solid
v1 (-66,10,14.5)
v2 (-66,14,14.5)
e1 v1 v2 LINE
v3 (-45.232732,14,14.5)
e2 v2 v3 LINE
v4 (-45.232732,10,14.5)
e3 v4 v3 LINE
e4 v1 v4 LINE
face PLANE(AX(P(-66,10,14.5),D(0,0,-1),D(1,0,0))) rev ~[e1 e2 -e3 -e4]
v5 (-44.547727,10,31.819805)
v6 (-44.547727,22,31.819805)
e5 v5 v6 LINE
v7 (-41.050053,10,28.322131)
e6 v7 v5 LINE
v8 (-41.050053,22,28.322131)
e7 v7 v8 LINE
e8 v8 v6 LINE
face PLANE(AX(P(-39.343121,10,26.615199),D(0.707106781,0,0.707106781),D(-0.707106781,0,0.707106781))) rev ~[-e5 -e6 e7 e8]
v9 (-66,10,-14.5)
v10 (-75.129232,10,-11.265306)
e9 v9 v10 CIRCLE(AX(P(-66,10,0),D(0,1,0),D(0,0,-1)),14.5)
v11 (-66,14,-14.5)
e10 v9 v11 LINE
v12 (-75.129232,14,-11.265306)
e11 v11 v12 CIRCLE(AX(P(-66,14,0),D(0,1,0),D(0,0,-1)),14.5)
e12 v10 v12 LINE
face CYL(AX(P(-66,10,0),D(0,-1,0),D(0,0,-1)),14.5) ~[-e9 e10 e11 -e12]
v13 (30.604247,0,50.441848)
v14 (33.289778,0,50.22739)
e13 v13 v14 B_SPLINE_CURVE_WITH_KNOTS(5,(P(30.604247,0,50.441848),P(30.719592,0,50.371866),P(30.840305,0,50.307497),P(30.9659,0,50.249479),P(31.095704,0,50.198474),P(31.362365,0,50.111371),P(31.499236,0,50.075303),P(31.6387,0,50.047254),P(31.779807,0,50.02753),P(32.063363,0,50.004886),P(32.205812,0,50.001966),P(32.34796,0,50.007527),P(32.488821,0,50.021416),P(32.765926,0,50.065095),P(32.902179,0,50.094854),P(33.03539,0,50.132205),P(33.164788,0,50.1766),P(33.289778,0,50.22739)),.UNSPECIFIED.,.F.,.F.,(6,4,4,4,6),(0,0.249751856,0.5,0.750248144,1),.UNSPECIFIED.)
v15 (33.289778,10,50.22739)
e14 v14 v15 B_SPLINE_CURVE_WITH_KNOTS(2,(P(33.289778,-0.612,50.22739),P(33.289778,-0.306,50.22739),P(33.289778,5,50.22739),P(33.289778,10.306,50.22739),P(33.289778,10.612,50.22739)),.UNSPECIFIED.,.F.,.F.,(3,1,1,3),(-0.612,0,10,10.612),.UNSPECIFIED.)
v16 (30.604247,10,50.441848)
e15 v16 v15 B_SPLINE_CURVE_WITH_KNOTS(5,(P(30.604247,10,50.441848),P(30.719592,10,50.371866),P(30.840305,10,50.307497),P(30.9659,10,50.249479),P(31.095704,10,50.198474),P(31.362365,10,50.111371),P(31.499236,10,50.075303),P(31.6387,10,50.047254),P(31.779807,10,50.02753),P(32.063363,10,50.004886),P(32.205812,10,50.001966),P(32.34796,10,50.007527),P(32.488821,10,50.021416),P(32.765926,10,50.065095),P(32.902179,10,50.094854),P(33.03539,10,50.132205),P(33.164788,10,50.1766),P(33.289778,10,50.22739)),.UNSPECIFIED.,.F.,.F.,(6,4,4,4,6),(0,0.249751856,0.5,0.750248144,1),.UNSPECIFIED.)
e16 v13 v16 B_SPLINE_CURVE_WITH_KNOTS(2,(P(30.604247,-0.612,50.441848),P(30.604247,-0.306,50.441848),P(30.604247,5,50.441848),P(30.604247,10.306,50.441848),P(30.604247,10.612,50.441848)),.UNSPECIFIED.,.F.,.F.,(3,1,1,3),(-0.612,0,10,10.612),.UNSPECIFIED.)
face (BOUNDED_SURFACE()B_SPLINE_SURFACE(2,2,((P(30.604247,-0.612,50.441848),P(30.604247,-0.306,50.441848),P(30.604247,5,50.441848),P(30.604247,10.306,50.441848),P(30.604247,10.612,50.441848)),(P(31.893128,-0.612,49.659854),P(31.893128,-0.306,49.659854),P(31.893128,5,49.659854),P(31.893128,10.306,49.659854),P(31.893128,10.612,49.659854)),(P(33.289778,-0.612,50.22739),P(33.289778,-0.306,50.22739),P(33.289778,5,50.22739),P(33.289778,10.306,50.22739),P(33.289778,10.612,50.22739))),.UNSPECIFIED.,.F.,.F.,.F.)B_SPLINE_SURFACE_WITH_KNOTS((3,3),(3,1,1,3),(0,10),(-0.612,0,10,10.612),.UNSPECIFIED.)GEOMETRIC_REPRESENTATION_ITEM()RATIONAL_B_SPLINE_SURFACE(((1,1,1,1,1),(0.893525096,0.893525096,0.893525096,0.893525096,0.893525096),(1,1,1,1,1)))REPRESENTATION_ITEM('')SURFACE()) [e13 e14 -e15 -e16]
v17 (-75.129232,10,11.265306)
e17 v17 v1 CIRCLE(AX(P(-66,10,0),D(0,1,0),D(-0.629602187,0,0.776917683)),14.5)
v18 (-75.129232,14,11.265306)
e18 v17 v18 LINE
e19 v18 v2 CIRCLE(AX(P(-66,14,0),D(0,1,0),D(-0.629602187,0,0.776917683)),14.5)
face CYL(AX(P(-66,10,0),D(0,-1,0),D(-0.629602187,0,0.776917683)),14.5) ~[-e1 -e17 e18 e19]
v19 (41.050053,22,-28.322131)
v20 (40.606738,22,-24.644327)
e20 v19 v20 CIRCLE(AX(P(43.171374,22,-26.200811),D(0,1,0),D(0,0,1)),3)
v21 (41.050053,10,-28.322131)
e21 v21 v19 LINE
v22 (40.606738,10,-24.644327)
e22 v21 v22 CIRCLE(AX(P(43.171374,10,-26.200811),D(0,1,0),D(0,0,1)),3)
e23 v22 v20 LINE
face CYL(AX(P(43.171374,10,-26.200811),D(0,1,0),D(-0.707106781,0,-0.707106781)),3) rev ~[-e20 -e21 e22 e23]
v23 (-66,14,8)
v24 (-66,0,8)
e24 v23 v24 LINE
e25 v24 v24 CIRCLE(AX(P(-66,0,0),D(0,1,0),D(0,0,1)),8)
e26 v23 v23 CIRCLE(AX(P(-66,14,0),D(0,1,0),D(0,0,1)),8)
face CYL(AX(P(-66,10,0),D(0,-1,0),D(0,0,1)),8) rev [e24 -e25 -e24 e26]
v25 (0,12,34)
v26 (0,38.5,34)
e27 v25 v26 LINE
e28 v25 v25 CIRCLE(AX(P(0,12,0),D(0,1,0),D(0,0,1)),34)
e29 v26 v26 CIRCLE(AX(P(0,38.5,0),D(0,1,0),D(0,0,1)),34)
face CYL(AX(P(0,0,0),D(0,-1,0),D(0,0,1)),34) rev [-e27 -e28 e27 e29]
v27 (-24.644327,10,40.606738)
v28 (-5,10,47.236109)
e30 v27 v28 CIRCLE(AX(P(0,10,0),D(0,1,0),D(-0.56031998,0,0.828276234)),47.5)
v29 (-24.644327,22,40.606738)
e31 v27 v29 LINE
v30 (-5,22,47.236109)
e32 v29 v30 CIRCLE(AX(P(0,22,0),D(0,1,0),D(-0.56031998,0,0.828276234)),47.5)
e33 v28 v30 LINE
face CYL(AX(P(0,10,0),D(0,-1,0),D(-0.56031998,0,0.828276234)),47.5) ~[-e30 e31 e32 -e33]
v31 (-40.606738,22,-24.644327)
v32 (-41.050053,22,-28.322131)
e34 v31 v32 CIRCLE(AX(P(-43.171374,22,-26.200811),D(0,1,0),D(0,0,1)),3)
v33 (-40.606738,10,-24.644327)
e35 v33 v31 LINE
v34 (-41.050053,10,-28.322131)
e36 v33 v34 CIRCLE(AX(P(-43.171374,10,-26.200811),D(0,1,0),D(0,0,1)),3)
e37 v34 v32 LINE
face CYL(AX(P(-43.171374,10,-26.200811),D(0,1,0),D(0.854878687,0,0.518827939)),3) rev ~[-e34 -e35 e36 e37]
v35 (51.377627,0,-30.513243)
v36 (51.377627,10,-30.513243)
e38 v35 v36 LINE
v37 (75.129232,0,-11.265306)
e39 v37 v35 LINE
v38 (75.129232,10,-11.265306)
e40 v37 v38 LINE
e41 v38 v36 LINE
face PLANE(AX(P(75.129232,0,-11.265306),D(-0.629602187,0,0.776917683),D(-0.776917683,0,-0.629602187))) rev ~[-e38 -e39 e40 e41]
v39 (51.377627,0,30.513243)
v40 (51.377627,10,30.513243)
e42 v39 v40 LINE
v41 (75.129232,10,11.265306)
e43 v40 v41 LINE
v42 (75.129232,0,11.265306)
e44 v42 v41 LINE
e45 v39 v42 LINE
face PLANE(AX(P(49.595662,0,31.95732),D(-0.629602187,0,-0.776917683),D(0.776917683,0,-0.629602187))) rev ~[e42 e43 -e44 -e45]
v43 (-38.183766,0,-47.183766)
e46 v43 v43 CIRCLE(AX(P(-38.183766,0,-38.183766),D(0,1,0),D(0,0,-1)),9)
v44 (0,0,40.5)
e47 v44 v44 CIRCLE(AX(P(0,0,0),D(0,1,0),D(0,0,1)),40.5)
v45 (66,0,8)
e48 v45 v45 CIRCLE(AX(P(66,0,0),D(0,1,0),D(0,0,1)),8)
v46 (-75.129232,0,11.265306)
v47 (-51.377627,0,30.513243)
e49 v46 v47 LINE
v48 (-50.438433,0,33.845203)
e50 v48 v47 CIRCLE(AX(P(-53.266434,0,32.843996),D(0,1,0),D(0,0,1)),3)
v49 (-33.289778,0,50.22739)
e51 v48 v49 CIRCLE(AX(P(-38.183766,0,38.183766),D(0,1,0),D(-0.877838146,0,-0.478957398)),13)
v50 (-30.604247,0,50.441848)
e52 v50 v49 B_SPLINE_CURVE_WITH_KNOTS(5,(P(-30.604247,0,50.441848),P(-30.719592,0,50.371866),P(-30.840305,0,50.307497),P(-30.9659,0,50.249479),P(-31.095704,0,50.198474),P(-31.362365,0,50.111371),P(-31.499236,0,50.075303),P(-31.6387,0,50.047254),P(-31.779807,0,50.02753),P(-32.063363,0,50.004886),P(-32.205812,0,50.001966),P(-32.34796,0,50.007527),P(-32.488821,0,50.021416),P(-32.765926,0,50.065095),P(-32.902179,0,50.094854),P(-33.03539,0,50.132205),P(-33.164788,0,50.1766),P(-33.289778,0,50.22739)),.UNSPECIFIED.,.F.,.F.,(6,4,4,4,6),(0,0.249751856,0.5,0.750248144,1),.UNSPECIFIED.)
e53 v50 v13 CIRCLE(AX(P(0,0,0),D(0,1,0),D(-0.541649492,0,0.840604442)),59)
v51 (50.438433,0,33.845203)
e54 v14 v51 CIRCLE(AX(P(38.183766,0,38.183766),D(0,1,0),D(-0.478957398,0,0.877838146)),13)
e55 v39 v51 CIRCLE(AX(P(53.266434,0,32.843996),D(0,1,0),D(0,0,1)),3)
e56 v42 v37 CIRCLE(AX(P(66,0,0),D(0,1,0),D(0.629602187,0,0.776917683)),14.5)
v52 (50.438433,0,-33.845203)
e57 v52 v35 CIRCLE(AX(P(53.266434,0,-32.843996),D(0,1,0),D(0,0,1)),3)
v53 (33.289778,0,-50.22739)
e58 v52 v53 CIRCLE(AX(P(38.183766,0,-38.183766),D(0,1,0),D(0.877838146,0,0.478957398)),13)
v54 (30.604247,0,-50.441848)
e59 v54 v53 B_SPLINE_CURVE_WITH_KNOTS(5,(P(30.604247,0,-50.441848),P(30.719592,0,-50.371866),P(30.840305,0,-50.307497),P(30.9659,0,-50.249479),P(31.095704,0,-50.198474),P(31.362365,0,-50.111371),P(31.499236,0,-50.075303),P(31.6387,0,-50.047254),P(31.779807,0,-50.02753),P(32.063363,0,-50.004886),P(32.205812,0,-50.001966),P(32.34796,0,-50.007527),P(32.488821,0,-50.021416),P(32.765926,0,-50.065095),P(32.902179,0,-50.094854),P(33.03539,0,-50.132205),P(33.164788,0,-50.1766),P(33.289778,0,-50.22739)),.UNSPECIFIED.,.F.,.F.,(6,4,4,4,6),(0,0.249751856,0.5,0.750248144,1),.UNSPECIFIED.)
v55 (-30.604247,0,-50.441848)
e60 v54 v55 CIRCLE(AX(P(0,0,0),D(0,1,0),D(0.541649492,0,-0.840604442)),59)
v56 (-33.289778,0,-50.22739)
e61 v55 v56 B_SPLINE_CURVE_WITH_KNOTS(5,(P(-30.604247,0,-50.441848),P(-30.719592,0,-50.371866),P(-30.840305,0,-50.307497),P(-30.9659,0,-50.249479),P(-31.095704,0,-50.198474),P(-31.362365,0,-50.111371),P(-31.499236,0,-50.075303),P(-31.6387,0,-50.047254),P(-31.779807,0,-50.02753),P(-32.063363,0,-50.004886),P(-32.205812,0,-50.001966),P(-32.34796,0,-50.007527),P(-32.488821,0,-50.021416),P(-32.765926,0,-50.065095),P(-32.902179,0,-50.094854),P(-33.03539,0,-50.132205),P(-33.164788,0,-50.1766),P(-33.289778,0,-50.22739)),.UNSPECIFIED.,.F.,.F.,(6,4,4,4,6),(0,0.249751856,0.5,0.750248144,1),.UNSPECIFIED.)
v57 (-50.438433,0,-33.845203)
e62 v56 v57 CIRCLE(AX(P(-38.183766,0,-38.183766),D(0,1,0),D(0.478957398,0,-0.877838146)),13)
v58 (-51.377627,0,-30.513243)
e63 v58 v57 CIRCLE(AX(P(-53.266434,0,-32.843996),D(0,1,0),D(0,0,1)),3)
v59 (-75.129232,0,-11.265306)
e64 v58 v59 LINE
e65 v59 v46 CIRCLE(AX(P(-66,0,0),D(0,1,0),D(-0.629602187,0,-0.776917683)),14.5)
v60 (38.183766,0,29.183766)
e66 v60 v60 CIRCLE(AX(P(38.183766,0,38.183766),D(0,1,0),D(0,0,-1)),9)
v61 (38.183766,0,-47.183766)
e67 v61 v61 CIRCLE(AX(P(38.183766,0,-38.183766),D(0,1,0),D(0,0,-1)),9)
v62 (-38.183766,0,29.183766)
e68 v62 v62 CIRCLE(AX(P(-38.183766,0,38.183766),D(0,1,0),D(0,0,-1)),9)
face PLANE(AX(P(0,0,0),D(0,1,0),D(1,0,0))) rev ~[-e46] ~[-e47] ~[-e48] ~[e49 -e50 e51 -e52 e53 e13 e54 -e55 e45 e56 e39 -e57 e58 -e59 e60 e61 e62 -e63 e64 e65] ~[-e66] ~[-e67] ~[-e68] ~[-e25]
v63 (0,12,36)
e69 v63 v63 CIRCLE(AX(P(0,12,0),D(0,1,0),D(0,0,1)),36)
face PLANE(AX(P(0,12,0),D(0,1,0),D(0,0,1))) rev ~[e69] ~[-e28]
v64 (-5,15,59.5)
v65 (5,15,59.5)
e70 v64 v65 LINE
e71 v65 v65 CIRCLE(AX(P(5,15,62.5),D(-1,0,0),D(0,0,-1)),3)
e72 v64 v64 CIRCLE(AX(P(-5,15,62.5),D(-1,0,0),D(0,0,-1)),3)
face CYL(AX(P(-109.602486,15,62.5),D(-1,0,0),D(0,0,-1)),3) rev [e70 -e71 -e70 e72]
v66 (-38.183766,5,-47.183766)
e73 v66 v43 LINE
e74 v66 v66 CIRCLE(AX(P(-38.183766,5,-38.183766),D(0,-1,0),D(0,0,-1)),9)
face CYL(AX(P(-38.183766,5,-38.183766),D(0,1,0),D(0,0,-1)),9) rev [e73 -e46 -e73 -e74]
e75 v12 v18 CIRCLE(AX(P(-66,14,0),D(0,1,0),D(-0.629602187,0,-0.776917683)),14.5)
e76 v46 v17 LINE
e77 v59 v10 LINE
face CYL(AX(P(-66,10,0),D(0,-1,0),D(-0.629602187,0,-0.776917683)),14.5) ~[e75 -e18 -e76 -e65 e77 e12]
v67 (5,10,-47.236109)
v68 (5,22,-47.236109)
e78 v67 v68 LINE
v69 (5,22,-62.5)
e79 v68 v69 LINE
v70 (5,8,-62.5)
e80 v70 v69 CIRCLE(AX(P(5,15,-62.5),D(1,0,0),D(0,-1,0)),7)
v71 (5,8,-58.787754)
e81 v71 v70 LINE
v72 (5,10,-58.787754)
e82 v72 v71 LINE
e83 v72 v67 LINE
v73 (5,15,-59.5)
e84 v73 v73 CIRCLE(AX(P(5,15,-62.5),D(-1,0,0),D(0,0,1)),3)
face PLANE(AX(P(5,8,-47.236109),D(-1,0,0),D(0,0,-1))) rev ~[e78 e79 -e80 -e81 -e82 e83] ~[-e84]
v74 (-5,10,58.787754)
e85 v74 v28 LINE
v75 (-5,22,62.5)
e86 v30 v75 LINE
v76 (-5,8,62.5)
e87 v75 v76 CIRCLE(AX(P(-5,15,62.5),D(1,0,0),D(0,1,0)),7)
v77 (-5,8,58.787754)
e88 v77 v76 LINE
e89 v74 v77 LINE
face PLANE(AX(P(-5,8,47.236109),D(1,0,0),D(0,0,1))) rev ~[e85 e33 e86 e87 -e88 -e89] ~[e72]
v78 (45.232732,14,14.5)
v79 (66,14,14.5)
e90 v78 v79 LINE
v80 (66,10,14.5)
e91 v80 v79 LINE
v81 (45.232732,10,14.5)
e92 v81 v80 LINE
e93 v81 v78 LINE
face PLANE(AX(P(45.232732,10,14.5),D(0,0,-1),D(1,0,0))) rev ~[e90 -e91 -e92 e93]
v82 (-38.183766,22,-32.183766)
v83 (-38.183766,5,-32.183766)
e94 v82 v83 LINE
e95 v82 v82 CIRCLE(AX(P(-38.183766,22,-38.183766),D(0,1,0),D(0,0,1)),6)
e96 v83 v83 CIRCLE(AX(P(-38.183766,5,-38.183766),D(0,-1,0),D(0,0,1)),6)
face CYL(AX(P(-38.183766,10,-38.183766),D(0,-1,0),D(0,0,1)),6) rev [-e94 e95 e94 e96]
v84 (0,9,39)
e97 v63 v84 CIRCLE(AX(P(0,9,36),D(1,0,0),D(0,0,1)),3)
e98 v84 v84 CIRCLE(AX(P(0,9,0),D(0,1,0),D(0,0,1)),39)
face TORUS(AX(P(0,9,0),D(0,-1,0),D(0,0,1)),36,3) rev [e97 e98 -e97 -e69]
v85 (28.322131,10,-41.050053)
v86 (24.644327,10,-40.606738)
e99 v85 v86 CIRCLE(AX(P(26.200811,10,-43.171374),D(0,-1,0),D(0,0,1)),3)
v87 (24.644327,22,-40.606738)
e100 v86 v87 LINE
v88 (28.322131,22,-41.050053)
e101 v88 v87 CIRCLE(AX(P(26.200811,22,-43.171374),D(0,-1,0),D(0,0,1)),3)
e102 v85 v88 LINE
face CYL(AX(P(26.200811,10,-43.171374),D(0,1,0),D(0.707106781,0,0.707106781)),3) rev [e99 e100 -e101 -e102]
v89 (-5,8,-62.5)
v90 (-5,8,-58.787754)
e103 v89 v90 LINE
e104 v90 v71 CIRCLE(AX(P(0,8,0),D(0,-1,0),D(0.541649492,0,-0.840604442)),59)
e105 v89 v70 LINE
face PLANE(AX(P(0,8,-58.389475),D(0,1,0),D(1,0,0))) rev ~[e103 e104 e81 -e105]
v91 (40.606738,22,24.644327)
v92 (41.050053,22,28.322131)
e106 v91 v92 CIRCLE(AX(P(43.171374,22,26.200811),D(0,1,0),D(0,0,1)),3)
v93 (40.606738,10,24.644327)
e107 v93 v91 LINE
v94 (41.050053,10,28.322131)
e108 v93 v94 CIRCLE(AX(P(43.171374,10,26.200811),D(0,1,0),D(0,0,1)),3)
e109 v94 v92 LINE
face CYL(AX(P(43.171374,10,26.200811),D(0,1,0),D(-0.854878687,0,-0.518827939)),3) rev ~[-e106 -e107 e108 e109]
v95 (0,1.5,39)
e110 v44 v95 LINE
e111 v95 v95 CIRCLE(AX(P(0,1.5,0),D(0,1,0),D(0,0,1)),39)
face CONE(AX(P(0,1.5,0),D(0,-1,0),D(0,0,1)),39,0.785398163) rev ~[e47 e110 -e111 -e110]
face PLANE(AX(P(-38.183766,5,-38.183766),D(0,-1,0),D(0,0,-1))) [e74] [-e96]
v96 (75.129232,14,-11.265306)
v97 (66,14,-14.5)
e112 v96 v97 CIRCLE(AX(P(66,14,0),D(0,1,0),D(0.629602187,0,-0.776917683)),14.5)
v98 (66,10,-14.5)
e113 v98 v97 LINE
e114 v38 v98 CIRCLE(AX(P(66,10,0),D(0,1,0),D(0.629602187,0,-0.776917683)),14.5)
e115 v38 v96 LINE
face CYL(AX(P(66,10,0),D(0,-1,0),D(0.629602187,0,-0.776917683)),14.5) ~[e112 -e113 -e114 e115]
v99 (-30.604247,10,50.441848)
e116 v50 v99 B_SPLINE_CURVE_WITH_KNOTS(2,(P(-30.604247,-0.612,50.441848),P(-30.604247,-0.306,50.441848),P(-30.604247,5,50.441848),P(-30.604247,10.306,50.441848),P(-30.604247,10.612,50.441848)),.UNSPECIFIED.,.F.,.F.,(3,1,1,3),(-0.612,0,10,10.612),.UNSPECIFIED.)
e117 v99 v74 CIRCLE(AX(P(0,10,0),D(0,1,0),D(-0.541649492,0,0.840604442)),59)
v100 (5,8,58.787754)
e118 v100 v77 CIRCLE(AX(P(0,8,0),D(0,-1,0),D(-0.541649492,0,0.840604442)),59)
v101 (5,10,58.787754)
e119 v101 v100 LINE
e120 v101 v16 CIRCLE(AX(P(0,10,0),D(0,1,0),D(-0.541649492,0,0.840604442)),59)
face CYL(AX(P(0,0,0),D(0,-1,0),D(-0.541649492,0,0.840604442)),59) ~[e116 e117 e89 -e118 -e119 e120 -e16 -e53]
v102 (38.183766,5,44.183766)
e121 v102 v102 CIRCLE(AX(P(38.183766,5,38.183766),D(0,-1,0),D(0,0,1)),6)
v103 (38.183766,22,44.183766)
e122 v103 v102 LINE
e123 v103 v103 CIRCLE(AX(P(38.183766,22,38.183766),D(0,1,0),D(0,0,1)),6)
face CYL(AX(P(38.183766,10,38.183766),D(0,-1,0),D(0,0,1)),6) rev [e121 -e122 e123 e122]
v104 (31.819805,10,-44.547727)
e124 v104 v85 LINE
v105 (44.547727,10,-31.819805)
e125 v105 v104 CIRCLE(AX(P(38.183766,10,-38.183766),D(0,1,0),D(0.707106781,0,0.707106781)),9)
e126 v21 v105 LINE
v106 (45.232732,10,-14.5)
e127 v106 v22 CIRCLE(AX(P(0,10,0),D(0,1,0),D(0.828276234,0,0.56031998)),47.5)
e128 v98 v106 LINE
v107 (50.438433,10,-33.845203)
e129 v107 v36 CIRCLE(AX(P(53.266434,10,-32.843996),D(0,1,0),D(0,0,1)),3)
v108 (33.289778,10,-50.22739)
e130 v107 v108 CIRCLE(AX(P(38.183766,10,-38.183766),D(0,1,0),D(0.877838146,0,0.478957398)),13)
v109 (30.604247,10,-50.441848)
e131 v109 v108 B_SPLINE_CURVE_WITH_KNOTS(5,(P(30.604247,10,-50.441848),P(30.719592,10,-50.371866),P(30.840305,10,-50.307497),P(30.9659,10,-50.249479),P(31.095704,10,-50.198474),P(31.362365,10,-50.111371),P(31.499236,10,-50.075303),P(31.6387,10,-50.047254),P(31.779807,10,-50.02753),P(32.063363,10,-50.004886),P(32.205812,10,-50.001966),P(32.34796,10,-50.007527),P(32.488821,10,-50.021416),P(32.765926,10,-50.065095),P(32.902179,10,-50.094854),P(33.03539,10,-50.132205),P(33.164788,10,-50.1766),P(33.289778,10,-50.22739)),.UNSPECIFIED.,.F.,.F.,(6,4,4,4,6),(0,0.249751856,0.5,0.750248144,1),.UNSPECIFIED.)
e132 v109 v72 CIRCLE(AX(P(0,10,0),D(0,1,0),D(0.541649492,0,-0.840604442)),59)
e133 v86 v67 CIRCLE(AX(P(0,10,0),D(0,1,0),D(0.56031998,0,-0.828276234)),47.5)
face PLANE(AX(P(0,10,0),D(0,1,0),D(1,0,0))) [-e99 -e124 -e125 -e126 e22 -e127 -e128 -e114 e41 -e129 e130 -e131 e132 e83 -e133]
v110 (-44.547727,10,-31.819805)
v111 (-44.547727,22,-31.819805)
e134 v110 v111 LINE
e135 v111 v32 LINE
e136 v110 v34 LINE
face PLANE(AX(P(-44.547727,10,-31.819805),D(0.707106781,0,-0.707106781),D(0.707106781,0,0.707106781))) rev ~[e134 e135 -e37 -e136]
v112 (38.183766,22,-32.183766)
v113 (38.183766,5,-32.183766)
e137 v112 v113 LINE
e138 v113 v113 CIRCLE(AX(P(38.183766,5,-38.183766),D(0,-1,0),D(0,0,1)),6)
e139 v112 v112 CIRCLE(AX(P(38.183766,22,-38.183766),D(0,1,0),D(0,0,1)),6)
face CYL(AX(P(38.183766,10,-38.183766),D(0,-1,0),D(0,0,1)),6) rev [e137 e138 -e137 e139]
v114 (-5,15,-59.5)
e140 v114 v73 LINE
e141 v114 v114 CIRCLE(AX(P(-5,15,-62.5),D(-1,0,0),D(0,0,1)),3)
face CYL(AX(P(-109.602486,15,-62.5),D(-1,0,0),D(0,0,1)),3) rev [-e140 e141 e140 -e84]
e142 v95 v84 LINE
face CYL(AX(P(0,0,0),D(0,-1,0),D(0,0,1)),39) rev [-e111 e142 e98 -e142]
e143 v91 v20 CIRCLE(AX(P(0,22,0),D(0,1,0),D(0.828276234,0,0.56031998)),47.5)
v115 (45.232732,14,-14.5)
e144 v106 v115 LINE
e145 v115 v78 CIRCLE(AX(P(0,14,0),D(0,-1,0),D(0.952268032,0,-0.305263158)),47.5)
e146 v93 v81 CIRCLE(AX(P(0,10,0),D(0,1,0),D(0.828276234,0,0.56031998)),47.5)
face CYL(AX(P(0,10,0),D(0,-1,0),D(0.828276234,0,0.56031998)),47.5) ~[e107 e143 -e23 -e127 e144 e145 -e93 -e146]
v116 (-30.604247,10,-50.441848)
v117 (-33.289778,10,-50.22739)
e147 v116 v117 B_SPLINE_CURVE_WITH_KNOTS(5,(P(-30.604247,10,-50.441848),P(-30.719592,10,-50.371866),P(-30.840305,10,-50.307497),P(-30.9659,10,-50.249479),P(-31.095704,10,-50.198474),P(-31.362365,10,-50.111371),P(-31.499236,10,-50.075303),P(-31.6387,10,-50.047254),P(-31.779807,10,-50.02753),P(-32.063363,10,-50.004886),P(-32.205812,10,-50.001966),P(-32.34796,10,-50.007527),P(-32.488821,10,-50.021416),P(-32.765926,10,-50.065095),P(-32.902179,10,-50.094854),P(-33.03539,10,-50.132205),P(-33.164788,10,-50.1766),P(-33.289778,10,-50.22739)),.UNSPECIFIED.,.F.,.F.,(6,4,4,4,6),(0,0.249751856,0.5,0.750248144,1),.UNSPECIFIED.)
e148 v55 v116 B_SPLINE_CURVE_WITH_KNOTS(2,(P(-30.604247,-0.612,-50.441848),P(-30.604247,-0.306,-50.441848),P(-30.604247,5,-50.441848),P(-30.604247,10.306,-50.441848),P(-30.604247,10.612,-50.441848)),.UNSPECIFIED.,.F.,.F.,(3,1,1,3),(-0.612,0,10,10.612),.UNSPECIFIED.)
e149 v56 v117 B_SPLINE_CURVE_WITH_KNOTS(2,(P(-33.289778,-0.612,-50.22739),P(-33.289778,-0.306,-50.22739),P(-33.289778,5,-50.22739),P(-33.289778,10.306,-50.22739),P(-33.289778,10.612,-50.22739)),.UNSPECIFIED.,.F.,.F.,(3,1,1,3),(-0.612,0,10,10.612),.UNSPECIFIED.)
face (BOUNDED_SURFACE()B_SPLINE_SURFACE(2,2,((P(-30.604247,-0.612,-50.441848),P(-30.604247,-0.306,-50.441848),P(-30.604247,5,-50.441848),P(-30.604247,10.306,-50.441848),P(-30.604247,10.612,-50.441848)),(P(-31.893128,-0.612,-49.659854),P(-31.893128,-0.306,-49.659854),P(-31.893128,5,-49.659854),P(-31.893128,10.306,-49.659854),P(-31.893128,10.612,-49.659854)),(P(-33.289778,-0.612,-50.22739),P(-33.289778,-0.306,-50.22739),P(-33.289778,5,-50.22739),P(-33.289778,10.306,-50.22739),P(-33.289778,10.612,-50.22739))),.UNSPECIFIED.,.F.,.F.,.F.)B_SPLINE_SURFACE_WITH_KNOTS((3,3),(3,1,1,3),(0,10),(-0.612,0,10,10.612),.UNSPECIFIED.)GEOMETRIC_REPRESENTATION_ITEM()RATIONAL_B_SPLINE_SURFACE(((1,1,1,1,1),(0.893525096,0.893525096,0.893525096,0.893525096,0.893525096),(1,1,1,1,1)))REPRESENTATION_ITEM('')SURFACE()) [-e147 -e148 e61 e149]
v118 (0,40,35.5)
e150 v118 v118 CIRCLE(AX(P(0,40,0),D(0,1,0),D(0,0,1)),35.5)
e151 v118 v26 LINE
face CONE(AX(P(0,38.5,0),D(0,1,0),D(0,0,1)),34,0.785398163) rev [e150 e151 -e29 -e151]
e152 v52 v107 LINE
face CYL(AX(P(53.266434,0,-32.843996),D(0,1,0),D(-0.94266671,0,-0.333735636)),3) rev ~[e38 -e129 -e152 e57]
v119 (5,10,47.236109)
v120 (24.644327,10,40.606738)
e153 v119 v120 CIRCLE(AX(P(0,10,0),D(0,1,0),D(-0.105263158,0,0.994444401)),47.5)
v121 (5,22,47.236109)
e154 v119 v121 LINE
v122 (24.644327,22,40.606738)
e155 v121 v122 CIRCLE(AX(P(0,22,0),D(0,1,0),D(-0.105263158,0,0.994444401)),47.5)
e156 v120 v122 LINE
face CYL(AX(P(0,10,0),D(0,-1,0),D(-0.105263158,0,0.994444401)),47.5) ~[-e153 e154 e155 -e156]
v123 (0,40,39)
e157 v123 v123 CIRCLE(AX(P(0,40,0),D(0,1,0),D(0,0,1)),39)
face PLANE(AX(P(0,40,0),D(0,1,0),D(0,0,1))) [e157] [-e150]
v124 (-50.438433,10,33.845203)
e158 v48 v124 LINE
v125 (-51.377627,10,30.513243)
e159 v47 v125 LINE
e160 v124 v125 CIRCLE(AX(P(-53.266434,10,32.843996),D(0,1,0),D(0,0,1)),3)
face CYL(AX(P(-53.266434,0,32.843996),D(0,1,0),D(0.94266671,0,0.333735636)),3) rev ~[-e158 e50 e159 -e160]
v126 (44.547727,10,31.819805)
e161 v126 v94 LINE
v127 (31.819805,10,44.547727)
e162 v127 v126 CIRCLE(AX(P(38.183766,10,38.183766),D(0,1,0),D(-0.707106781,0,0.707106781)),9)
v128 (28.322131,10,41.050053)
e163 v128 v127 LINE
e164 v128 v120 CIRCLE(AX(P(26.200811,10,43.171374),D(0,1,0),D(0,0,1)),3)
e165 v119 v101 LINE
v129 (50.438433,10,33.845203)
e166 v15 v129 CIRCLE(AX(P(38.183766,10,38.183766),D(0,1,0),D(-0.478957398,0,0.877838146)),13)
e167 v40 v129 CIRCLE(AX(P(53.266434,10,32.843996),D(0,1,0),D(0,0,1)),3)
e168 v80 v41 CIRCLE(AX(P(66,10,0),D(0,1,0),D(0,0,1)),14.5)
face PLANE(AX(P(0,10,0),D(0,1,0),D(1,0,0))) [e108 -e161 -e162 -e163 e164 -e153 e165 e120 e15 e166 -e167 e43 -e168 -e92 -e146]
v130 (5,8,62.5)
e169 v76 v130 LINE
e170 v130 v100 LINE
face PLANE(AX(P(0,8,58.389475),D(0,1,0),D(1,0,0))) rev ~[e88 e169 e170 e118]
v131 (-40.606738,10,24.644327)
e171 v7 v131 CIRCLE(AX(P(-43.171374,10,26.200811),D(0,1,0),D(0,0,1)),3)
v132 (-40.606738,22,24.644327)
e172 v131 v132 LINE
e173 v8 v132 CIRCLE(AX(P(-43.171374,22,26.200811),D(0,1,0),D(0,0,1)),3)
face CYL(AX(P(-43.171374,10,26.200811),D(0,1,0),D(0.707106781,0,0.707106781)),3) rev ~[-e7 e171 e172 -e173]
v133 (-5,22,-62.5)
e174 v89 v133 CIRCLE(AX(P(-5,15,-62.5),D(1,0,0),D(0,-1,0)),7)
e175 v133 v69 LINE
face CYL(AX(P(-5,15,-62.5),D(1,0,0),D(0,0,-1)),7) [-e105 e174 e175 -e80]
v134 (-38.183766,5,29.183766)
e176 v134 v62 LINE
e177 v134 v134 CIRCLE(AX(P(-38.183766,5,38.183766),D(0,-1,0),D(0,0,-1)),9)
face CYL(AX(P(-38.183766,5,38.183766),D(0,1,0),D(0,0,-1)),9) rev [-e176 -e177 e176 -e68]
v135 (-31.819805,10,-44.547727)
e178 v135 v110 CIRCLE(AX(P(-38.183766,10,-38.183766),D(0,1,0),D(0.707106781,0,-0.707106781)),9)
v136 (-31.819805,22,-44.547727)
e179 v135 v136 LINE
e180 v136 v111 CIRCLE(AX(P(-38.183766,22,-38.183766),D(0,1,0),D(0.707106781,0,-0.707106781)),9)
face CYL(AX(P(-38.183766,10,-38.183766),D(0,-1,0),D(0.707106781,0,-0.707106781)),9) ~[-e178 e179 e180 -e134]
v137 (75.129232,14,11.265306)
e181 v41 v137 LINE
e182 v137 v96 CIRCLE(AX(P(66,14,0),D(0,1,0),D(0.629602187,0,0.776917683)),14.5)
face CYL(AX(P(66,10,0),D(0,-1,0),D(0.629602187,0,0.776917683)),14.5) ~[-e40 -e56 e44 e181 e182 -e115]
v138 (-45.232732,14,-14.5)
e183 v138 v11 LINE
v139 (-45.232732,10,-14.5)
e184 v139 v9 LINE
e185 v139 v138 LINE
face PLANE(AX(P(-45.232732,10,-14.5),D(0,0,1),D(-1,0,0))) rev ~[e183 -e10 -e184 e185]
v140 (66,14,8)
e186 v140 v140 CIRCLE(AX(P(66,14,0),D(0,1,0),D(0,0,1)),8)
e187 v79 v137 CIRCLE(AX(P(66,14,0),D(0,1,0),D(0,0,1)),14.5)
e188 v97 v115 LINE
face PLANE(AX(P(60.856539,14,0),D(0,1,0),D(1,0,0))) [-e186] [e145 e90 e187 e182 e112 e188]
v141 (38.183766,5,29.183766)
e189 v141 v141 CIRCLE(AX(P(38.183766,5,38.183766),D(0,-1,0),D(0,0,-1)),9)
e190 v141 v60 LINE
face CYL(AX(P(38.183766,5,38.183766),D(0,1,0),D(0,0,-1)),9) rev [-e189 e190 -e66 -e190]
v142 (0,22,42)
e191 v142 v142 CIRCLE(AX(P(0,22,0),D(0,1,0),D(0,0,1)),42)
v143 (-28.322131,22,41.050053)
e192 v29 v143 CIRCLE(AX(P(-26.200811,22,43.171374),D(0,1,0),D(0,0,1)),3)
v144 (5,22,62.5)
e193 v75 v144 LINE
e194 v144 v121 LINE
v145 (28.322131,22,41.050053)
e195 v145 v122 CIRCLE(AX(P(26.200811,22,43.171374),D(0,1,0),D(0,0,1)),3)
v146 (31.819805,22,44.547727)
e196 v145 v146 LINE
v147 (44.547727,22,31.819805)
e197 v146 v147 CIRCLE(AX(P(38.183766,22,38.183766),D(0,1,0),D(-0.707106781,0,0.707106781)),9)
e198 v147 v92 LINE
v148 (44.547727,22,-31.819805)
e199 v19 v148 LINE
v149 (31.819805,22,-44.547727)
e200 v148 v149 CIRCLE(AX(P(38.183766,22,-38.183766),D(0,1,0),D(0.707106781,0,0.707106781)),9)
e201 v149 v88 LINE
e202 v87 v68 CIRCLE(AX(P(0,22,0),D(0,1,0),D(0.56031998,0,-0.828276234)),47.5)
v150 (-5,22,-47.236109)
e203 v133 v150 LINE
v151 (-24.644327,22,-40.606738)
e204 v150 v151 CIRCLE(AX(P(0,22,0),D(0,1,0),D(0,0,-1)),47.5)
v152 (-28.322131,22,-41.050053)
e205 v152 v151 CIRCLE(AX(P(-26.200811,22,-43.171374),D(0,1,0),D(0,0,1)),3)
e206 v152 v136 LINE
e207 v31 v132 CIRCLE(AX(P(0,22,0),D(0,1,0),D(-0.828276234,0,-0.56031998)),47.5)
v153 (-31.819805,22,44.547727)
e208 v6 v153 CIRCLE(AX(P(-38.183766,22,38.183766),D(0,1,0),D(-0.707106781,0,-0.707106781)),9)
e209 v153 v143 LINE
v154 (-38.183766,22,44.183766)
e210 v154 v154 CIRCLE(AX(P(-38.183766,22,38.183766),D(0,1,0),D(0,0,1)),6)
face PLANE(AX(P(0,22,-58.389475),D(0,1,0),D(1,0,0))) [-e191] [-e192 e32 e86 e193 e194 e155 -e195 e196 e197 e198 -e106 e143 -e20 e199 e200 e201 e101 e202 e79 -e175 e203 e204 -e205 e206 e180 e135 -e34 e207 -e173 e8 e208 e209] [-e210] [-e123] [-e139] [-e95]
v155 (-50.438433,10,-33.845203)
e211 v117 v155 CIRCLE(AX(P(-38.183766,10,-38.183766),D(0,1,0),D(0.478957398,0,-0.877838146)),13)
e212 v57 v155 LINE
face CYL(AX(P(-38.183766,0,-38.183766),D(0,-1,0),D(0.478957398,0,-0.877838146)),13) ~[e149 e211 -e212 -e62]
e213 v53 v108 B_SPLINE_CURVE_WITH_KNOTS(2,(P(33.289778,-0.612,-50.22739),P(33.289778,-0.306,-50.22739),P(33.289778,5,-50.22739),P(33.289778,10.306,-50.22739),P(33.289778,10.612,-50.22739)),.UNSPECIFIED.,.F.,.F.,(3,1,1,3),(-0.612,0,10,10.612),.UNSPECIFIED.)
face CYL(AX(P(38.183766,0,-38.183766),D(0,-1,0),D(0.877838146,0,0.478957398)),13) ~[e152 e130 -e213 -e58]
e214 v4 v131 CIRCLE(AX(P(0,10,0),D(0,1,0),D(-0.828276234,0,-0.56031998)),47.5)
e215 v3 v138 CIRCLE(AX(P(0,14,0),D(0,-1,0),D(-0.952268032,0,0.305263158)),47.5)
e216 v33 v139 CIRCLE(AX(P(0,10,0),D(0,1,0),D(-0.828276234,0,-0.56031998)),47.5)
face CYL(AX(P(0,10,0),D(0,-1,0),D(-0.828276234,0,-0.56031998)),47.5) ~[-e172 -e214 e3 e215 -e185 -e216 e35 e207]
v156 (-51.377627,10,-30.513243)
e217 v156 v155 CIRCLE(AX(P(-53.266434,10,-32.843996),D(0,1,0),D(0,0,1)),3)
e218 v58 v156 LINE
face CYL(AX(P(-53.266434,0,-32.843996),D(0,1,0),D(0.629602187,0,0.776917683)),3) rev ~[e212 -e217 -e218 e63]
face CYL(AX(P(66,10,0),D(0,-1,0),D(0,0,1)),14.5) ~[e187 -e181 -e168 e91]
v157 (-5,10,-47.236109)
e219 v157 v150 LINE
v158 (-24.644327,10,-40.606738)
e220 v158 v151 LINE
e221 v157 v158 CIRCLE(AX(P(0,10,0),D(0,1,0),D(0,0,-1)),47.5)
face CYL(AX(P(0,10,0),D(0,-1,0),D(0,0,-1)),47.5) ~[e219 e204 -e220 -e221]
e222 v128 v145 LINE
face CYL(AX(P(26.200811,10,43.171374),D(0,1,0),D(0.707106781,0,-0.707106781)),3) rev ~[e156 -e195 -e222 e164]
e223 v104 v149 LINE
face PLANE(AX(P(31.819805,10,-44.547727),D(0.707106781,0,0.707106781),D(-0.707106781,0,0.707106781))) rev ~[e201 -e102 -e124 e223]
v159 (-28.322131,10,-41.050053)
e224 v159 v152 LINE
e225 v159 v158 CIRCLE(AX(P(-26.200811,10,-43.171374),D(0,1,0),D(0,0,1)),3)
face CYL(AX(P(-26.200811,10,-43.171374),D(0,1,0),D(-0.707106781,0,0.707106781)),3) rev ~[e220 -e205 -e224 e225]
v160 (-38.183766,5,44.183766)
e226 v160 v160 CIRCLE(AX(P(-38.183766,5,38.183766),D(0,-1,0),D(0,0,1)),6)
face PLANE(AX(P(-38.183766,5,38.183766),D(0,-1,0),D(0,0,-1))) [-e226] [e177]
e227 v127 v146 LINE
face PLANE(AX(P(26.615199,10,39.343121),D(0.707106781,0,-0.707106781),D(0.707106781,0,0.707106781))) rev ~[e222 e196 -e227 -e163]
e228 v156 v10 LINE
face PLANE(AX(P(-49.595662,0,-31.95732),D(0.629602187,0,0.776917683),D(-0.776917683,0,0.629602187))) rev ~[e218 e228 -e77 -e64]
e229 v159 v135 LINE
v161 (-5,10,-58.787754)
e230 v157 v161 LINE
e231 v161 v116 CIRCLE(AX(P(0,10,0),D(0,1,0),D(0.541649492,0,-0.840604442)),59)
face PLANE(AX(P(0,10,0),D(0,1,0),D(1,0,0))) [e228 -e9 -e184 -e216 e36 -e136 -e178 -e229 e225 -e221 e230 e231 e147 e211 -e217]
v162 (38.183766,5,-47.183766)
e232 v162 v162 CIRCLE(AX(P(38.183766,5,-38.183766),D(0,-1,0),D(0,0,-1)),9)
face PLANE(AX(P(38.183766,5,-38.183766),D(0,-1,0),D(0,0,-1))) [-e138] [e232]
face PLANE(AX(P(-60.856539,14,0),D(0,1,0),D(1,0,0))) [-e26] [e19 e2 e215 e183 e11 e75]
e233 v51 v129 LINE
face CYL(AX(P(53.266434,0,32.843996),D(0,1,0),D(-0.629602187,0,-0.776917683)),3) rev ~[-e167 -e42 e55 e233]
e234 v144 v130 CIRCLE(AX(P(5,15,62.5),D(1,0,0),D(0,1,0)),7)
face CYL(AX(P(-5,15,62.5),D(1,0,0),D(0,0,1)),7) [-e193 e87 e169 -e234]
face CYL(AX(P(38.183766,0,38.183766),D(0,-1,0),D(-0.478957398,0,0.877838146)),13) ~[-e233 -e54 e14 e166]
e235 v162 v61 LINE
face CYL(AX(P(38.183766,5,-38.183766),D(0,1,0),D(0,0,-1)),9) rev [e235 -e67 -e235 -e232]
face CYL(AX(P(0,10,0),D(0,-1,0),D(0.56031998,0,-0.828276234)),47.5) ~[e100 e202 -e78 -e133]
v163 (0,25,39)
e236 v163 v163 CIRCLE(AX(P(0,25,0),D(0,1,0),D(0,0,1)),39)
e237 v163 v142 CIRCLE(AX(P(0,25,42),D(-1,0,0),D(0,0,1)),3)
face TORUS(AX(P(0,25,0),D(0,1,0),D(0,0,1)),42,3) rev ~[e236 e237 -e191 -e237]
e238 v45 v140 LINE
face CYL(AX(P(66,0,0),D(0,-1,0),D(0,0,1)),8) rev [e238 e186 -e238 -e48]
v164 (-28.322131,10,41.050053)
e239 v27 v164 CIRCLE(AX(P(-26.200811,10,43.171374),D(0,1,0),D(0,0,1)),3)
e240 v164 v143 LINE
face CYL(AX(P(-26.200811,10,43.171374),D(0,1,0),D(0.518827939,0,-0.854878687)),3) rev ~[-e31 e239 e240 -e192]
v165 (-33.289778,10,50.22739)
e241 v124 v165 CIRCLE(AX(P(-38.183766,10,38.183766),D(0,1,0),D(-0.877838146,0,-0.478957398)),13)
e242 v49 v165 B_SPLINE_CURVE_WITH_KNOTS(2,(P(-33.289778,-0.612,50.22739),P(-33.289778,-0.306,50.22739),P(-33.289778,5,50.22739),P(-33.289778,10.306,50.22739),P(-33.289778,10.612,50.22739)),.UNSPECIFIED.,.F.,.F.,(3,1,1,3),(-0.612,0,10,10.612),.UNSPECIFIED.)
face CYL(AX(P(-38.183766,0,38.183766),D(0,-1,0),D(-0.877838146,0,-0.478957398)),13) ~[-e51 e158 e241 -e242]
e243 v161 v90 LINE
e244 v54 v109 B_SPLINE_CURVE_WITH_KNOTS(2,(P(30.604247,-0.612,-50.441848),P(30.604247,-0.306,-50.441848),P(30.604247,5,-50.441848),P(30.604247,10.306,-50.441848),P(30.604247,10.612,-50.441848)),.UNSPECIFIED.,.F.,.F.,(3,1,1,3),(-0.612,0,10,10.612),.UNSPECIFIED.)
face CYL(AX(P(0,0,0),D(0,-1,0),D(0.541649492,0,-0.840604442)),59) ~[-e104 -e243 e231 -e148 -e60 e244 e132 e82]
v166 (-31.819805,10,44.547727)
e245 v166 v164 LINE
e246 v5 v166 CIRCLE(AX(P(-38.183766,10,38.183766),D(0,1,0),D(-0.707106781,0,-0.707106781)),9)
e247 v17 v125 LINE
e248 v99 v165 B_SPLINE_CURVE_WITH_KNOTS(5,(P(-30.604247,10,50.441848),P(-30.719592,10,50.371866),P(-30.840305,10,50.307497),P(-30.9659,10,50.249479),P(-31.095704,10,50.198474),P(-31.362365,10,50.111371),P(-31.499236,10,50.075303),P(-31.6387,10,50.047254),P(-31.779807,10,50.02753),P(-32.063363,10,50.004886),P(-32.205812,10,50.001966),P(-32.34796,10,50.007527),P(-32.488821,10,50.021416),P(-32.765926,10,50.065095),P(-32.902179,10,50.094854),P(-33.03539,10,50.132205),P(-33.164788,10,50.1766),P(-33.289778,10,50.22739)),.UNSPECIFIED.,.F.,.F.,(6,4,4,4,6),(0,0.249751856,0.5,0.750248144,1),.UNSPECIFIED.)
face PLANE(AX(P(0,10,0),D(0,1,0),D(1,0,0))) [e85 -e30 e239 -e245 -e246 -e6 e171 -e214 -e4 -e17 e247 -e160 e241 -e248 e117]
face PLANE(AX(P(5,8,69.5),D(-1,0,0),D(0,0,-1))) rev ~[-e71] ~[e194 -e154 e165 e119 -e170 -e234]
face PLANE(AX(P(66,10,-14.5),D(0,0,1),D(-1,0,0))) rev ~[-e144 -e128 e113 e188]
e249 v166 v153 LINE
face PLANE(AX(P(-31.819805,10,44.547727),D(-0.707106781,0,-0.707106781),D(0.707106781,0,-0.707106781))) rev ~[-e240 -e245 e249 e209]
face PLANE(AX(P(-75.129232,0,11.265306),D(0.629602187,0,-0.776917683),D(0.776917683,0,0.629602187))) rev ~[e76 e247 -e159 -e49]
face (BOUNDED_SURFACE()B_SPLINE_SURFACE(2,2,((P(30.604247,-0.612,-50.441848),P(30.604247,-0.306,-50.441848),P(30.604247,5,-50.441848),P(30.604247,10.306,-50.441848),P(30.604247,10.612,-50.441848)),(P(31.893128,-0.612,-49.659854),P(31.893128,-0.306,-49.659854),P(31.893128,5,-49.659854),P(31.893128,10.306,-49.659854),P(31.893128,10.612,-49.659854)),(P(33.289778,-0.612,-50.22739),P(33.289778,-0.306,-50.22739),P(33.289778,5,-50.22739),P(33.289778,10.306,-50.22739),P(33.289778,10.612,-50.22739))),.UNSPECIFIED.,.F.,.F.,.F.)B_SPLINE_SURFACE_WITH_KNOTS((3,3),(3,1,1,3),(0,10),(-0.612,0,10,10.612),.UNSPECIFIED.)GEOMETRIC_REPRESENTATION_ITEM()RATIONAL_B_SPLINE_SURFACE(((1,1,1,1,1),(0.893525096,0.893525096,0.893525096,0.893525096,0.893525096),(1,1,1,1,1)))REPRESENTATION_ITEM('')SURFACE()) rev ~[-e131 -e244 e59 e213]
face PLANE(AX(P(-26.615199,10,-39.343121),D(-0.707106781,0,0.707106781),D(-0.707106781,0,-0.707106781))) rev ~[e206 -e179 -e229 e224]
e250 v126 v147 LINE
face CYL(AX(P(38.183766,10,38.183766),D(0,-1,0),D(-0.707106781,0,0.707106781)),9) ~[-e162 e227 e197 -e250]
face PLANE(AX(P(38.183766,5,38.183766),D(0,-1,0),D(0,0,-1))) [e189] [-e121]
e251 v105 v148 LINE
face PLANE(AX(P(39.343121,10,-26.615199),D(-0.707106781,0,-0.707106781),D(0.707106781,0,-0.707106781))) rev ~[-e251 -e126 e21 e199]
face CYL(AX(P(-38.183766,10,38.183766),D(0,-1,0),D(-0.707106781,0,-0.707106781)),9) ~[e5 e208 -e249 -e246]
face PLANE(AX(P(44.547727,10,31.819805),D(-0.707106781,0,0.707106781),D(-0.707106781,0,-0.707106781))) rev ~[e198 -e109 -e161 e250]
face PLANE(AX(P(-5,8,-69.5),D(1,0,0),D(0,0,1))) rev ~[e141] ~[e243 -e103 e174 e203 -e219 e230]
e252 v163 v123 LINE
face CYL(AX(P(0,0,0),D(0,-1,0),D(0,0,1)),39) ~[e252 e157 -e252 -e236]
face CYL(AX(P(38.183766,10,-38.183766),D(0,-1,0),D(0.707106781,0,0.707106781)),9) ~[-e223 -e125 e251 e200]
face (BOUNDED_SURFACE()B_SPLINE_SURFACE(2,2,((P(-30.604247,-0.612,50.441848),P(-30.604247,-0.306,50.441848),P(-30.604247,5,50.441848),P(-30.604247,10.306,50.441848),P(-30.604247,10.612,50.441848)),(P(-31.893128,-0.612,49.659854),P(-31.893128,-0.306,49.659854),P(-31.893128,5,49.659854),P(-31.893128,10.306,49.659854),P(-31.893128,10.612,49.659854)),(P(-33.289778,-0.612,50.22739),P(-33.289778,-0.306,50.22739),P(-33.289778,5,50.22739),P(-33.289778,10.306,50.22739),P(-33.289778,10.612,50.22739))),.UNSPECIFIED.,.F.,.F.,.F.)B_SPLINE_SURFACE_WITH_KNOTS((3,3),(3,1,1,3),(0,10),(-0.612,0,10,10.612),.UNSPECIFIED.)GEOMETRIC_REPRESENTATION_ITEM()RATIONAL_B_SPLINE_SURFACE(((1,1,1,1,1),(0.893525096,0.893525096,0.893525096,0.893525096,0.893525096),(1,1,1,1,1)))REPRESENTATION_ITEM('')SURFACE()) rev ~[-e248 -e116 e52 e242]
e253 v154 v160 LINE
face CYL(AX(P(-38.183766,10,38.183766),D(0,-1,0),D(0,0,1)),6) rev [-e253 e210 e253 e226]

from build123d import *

# Parameters (mm, degrees)
HOUSING_MASTER_SKETCH_R        = 6
HOUSING_MASTER_SKETCH_R_2      = 39
HOUSING_MASTER_SKETCH_R_3      = 8
FLANGE_PLATE_10MM_DEPTH        = 10
RAISED_START                   = 10
SKETCH1_3_R                    = 8
RAISED_PADS_4MM_DEPTH          = 4
MOUNTING_START                 = 10
SKETCH1_4_R                    = 39
SKETCH1_4_R_2                  = 6
MOUNTING_BOSSES_12MM_DEPTH     = 12
HUB_START                      = 8
HUB_COLLAR_14MM_DEPTH          = 14
HUB_COLLAR_FILLET_A_RADIUS     = 7
HUB_COLLAR_FILLET_A_LENGTH     = 10
HUB_COLLAR_FILLET_B_RADIUS     = 7
HUB_COLLAR_FILLET_B_LENGTH     = 10
LUG_CROSS_HOLES_DEPTH          = 109.602486159
LUG_CROSS_HOLES_DEPTH_BACK     = 109.602486159
LUG_CROSS_HOLE_SKETCH_R        = 3
SKETCH1_7_R                    = 39
SKETCH1_7_R_2                  = 34
SPIGOT_TUBE_40MM_DEPTH         = 40
FLANGE_SLOT_CUT_5MM_DEPTH      = 114.624381186
FLANGE_SLOT_CUT_5MM_DEPTH_BACK = 5
FLANGE_SLOT_SKETCH_R           = 9
SKETCH1_9_R                    = 39
SKETCH1_9_R_2                  = 34
SPIGOT_BORE_CUT_DEPTH          = 12
SPIGOT_CHAMFER_1_5X45_SIZE     = 1.5
BLEND_FILLETS_R3_R             = 3


with BuildPart() as part:
    # Housing Master Sketch → Flange Plate 10mm (new body)
    with BuildSketch(Plane(origin=(0, 0, 0), x_dir=(1, 0, 0), z_dir=(0, 1, 0))):
        with BuildLine():
            Line((75.129231708, 11.265306406), (49.595662085, 31.957320012))
            ThreePointArc((49.595662085, 31.957320012), (47.376154339, 47.376154339), (31.957320012, 49.595662085))
            ThreePointArc((31.957320012, 49.595662085), (0, 59), (-31.957320012, 49.595662085))
            ThreePointArc((-31.957320012, 49.595662085), (-47.376154339, 47.376154339), (-49.595662085, 31.957320012))
            Line((-49.595662085, 31.957320012), (-75.129231708, 11.265306406))
            ThreePointArc((-75.129231708, 11.265306406), (-80.5, 0), (-75.129231708, -11.265306406))
            Line((-75.129231708, -11.265306406), (-49.595662085, -31.957320012))
            ThreePointArc((-49.595662085, -31.957320012), (-47.376154339, -47.376154339), (-31.957320012, -49.595662085))
            ThreePointArc((-31.957320012, -49.595662085), (0, -59), (31.957320012, -49.595662085))
            ThreePointArc((31.957320012, -49.595662085), (47.376154339, -47.376154339), (49.595662085, -31.957320012))
            Line((49.595662085, -31.957320012), (75.129231708, -11.265306406))
            ThreePointArc((75.129231708, -11.265306406), (80.5, 0), (75.129231708, 11.265306406))
        make_face()
        with Locations(Location((-38.183766184, -38.183766184, 0), (0, 0, 270))):
            Circle(HOUSING_MASTER_SKETCH_R, mode=Mode.SUBTRACT)
        with Locations(Location((38.183766184, -38.183766184, 0), (0, 0, 270))):
            Circle(HOUSING_MASTER_SKETCH_R, mode=Mode.SUBTRACT)
        with Locations(Location((0, 0, 0), (0, 0, 270))):
            Circle(HOUSING_MASTER_SKETCH_R_2, mode=Mode.SUBTRACT)
        with Locations(Location((-38.183766184, 38.183766184, 0), (0, 0, 270))):
            Circle(HOUSING_MASTER_SKETCH_R, mode=Mode.SUBTRACT)
        with Locations(Location((38.183766184, 38.183766184, 0), (0, 0, 270))):
            Circle(HOUSING_MASTER_SKETCH_R, mode=Mode.SUBTRACT)
        with Locations(Location((66, 0, 0), (0, 0, 270))):
            Circle(HOUSING_MASTER_SKETCH_R_3, mode=Mode.SUBTRACT)
        with Locations(Location((-66, 0, 0), (0, 0, 270))):
            Circle(HOUSING_MASTER_SKETCH_R_3, mode=Mode.SUBTRACT)
    extrude(amount=FLANGE_PLATE_10MM_DEPTH)

    # Sketch1_3 → Raised Pads 4mm (add)
    # profile 1 of 2: a face of its own
    with BuildSketch(Plane(origin=(0, 0, 0), x_dir=(1, 0, 0), z_dir=(0, 1, 0)).offset(RAISED_START)):
        with BuildLine():
            ThreePointArc((-66, 14.5), (-70.842677829, 13.667423731), (-75.129231708, 11.265306406))
            ThreePointArc((-75.129231708, 11.265306406), (-80.5, 0), (-75.129231708, -11.265306406))
            ThreePointArc((-75.129231708, -11.265306406), (-70.842677829, -13.667423731), (-66, -14.5))
            Line((-66, -14.5), (-45.232731512, -14.5))
            ThreePointArc((-45.232731512, -14.5), (-47.5, 0), (-45.232731512, 14.5))
            Line((-45.232731512, 14.5), (-66, 14.5))
        make_face()
        with Locations(Location((-66, 0, 0), (0, 0, 270))):
            Circle(SKETCH1_3_R, mode=Mode.SUBTRACT)
    # profile 2 of 2: a face of its own
    with BuildSketch(Plane(origin=(0, 0, 0), x_dir=(1, 0, 0), z_dir=(0, 1, 0)).offset(RAISED_START)):
        with BuildLine():
            Line((66, 14.5), (45.232731512, 14.5))
            ThreePointArc((45.232731512, 14.5), (47.5, 0), (45.232731512, -14.5))
            Line((45.232731512, -14.5), (66, -14.5))
            ThreePointArc((66, -14.5), (70.842677829, -13.667423731), (75.129231708, -11.265306406))
            ThreePointArc((75.129231708, -11.265306406), (80.5, 0), (75.129231708, 11.265306406))
            ThreePointArc((75.129231708, 11.265306406), (70.842677829, 13.667423731), (66, 14.5))
        make_face()
        with Locations(Location((66, 0, 0), (0, 0, 270))):
            Circle(SKETCH1_3_R, mode=Mode.SUBTRACT)
    extrude(amount=RAISED_PADS_4MM_DEPTH)



with BuildPart() as body_2:
    # Sketch1_4 → Mounting Bosses 12mm (new body)
    with BuildSketch(Plane(origin=(0, 0, 0), x_dir=(1, 0, 0), z_dir=(0, 1, 0)).offset(MOUNTING_START)):
        with BuildLine():
            Line((39.343121117, 26.615199056), (44.547727215, 31.819805153))
            ThreePointArc((44.547727215, 31.819805153), (44.547727215, 44.547727215), (31.819805153, 44.547727215))
            Line((31.819805153, 44.547727215), (26.615199056, 39.343121117))
            ThreePointArc((26.615199056, 39.343121117), (13.91854423, 45.415020935), (0, 47.5))
            ThreePointArc((0, 47.5), (-13.91854423, 45.415020935), (-26.615199056, 39.343121117))
            Line((-26.615199056, 39.343121117), (-31.819805153, 44.547727215))
            ThreePointArc((-31.819805153, 44.547727215), (-44.547727215, 44.547727215), (-44.547727215, 31.819805153))
            Line((-44.547727215, 31.819805153), (-39.343121117, 26.615199056))
            ThreePointArc((-39.343121117, 26.615199056), (-47.5, 0), (-39.343121117, -26.615199056))
            Line((-39.343121117, -26.615199056), (-44.547727215, -31.819805153))
            ThreePointArc((-44.547727215, -31.819805153), (-44.547727215, -44.547727215), (-31.819805153, -44.547727215))
            Line((-31.819805153, -44.547727215), (-26.615199056, -39.343121117))
            ThreePointArc((-26.615199056, -39.343121117), (-16.292790354, -44.618325635), (-5, -47.236109069))
            ThreePointArc((-5, -47.236109069), (11.505608296, -46.085474694), (26.615199056, -39.343121117))
            Line((26.615199056, -39.343121117), (31.819805153, -44.547727215))
            ThreePointArc((31.819805153, -44.547727215), (44.547727215, -44.547727215), (44.547727215, -31.819805153))
            Line((44.547727215, -31.819805153), (39.343121117, -26.615199056))
            ThreePointArc((39.343121117, -26.615199056), (47.5, 0), (39.343121117, 26.615199056))
        make_face()
        with Locations(Location((0, 0, 0), (0, 0, 270))):
            Circle(SKETCH1_4_R, mode=Mode.SUBTRACT)
        with Locations(Location((38.183766184, 38.183766184, 0), (0, 0, 270))):
            Circle(SKETCH1_4_R_2, mode=Mode.SUBTRACT)
        with Locations(Location((38.183766184, -38.183766184, 0), (0, 0, 270))):
            Circle(SKETCH1_4_R_2, mode=Mode.SUBTRACT)
        with Locations(Location((-38.183766184, -38.183766184, 0), (0, 0, 270))):
            Circle(SKETCH1_4_R_2, mode=Mode.SUBTRACT)
        with Locations(Location((-38.183766184, 38.183766184, 0), (0, 0, 270))):
            Circle(SKETCH1_4_R_2, mode=Mode.SUBTRACT)
    extrude(amount=MOUNTING_BOSSES_12MM_DEPTH)


with BuildPart() as part_1:
    add(part.part)

    add(body_2.part)  # Hub Collar 14mm merges body 2
    # Sketch1_6 → Hub Collar 14mm (add)
    with BuildSketch(Plane(origin=(0, 0, 0), x_dir=(1, 0, 0), z_dir=(0, 1, 0)).offset(HUB_START)):
        with BuildLine():
            Line((5, 47.236109069), (5, 69.5))
            Line((5, 69.5), (-5, 69.5))
            Line((-5, 69.5), (-5, 47.236109069))
            ThreePointArc((-5, 47.236109069), (0, 47.5), (5, 47.236109069))
        make_face()
        with BuildLine():
            Line((-5, -47.236109069), (-5, -69.5))
            Line((-5, -69.5), (5, -69.5))
            Line((5, -69.5), (5, -47.236109069))
            ThreePointArc((5, -47.236109069), (0, -47.5), (-5, -47.236109069))
        make_face()
    extrude(amount=HUB_COLLAR_14MM_DEPTH)

    # Hub Collar Fillet A: full round fillet: the end face becomes a half cylinder, R = half its width
    hub_collar_fillet_a_face = Plane((0, 15, 69.5), x_dir=(1, 0, 0), z_dir=(0, 0, 1))  # on the end face: x along it, z out of the body
    hub_collar_fillet_a_slab = hub_collar_fillet_a_face.offset(-HUB_COLLAR_FILLET_A_RADIUS / 2) * Box(HUB_COLLAR_FILLET_A_LENGTH, 2 * HUB_COLLAR_FILLET_A_RADIUS, HUB_COLLAR_FILLET_A_RADIUS, mode=Mode.PRIVATE)  # the body's end, R deep
    hub_collar_fillet_a_round = Plane((0, 15, 62.5), x_dir=(0, 0, 1), z_dir=(1, 0, 0)) * Cylinder(HUB_COLLAR_FILLET_A_RADIUS, HUB_COLLAR_FILLET_A_LENGTH, mode=Mode.PRIVATE)  # its axis R under the face
    add(hub_collar_fillet_a_slab - hub_collar_fillet_a_round, mode=Mode.SUBTRACT)

    # Hub Collar Fillet B: full round fillet: the end face becomes a half cylinder, R = half its width
    hub_collar_fillet_b_face = Plane((0, 15, -69.5), x_dir=(1, 0, 0), z_dir=(0, 0, -1))  # on the end face: x along it, z out of the body
    hub_collar_fillet_b_slab = hub_collar_fillet_b_face.offset(-HUB_COLLAR_FILLET_B_RADIUS / 2) * Box(HUB_COLLAR_FILLET_B_LENGTH, 2 * HUB_COLLAR_FILLET_B_RADIUS, HUB_COLLAR_FILLET_B_RADIUS, mode=Mode.PRIVATE)  # the body's end, R deep
    hub_collar_fillet_b_round = Plane((0, 15, -62.5), x_dir=(0, 0, -1), z_dir=(1, 0, 0)) * Cylinder(HUB_COLLAR_FILLET_B_RADIUS, HUB_COLLAR_FILLET_B_LENGTH, mode=Mode.PRIVATE)  # its axis R under the face
    add(hub_collar_fillet_b_slab - hub_collar_fillet_b_round, mode=Mode.SUBTRACT)

    # Lug Cross Hole Sketch → Lug Cross Holes (cut, two sides: drawn at the far end of the back side and taken through both)
    with BuildSketch(Plane(origin=(0, 0, 0), x_dir=(0, 0, -1), z_dir=(1, 0, 0)).offset(-LUG_CROSS_HOLES_DEPTH_BACK)):
        with Locations((-62.5, 15)):
            Circle(LUG_CROSS_HOLE_SKETCH_R)
        with Locations(Location((62.5, 15, 0), (0, 0, 180))):
            Circle(LUG_CROSS_HOLE_SKETCH_R)
    extrude(amount=LUG_CROSS_HOLES_DEPTH + LUG_CROSS_HOLES_DEPTH_BACK, mode=Mode.SUBTRACT)

    # Sketch1_7 → Spigot Tube 40mm (add)
    with BuildSketch(Plane(origin=(0, 0, 0), x_dir=(1, 0, 0), z_dir=(0, 1, 0))):
        with Locations(Location((0, 0, 0), (0, 0, 270))):
            Circle(SKETCH1_7_R)
        with Locations(Location((0, 0, 0), (0, 0, 270))):
            Circle(SKETCH1_7_R_2, mode=Mode.SUBTRACT)
    extrude(amount=SPIGOT_TUBE_40MM_DEPTH)

    # Flange Slot Sketch → Flange Slot Cut 5mm (cut, two sides: drawn at the far end of the back side and taken through both)
    with BuildSketch(Plane.XZ.offset(-FLANGE_SLOT_CUT_5MM_DEPTH_BACK)):
        with Locations(Location((-38.183766184, 38.183766184, 0), (0, 0, 270))):
            Circle(FLANGE_SLOT_SKETCH_R)
        with Locations(Location((38.183766184, 38.183766184, 0), (0, 0, 270))):
            Circle(FLANGE_SLOT_SKETCH_R)
        with Locations(Location((38.183766184, -38.183766184, 0), (0, 0, 270))):
            Circle(FLANGE_SLOT_SKETCH_R)
        with Locations(Location((-38.183766184, -38.183766184, 0), (0, 0, 270))):
            Circle(FLANGE_SLOT_SKETCH_R)
    extrude(amount=FLANGE_SLOT_CUT_5MM_DEPTH + FLANGE_SLOT_CUT_5MM_DEPTH_BACK, mode=Mode.SUBTRACT)

    # Sketch1_9 → Spigot Bore Cut (cut)
    with BuildSketch(Plane(origin=(0, 0, 0), x_dir=(1, 0, 0), z_dir=(0, 1, 0))):
        with Locations(Location((0, 0, 0), (0, 0, 270))):
            Circle(SKETCH1_9_R)
        with Locations(Location((0, 0, 0), (0, 0, 270))):
            Circle(SKETCH1_9_R_2, mode=Mode.SUBTRACT)
    extrude(amount=SPIGOT_BORE_CUT_DEPTH, mode=Mode.SUBTRACT)

    # Spigot Chamfer 1.5x45
    spigot_chamfer_1_5x45_edges = [part_1.edges().sort_by_distance(p)[0] for p in [
        (0, 40, -34),
        (0, 0, -39),
    ]]
    chamfer(spigot_chamfer_1_5x45_edges, length=SPIGOT_CHAMFER_1_5X45_SIZE)

    # Blend Fillets R3
    blend_fillets_r3_edges = [part_1.edges().sort_by_distance(p)[0] for p in [
        (-26.615199056, 16, 39.343121117),
        (26.615199056, 16, 39.343121117),
        (39.343121117, 16, 26.615199056),
        (39.343121117, 16, -26.615199056),
        (26.615199056, 16, -39.343121117),
        (-26.615199056, 16, -39.343121117),
        (-39.343121117, 16, -26.615199056),
        (-39.343121117, 16, 26.615199056),
        (0, 22, -39),
        (0, 12, -39),
        (49.595662085, 5, 31.957320012),
        (31.957320012, 5, 49.595662085),
        (-31.957320012, 5, 49.595662085),
        (-49.595662085, 5, 31.957320012),
        (-49.595662085, 5, -31.957320012),
        (-31.957320012, 5, -49.595662085),
        (31.957320012, 5, -49.595662085),
        (49.595662085, 5, -31.957320012),
    ]]
    fillet(blend_fillets_r3_edges, radius=BLEND_FILLETS_R3_R)


solid = part_1.part
